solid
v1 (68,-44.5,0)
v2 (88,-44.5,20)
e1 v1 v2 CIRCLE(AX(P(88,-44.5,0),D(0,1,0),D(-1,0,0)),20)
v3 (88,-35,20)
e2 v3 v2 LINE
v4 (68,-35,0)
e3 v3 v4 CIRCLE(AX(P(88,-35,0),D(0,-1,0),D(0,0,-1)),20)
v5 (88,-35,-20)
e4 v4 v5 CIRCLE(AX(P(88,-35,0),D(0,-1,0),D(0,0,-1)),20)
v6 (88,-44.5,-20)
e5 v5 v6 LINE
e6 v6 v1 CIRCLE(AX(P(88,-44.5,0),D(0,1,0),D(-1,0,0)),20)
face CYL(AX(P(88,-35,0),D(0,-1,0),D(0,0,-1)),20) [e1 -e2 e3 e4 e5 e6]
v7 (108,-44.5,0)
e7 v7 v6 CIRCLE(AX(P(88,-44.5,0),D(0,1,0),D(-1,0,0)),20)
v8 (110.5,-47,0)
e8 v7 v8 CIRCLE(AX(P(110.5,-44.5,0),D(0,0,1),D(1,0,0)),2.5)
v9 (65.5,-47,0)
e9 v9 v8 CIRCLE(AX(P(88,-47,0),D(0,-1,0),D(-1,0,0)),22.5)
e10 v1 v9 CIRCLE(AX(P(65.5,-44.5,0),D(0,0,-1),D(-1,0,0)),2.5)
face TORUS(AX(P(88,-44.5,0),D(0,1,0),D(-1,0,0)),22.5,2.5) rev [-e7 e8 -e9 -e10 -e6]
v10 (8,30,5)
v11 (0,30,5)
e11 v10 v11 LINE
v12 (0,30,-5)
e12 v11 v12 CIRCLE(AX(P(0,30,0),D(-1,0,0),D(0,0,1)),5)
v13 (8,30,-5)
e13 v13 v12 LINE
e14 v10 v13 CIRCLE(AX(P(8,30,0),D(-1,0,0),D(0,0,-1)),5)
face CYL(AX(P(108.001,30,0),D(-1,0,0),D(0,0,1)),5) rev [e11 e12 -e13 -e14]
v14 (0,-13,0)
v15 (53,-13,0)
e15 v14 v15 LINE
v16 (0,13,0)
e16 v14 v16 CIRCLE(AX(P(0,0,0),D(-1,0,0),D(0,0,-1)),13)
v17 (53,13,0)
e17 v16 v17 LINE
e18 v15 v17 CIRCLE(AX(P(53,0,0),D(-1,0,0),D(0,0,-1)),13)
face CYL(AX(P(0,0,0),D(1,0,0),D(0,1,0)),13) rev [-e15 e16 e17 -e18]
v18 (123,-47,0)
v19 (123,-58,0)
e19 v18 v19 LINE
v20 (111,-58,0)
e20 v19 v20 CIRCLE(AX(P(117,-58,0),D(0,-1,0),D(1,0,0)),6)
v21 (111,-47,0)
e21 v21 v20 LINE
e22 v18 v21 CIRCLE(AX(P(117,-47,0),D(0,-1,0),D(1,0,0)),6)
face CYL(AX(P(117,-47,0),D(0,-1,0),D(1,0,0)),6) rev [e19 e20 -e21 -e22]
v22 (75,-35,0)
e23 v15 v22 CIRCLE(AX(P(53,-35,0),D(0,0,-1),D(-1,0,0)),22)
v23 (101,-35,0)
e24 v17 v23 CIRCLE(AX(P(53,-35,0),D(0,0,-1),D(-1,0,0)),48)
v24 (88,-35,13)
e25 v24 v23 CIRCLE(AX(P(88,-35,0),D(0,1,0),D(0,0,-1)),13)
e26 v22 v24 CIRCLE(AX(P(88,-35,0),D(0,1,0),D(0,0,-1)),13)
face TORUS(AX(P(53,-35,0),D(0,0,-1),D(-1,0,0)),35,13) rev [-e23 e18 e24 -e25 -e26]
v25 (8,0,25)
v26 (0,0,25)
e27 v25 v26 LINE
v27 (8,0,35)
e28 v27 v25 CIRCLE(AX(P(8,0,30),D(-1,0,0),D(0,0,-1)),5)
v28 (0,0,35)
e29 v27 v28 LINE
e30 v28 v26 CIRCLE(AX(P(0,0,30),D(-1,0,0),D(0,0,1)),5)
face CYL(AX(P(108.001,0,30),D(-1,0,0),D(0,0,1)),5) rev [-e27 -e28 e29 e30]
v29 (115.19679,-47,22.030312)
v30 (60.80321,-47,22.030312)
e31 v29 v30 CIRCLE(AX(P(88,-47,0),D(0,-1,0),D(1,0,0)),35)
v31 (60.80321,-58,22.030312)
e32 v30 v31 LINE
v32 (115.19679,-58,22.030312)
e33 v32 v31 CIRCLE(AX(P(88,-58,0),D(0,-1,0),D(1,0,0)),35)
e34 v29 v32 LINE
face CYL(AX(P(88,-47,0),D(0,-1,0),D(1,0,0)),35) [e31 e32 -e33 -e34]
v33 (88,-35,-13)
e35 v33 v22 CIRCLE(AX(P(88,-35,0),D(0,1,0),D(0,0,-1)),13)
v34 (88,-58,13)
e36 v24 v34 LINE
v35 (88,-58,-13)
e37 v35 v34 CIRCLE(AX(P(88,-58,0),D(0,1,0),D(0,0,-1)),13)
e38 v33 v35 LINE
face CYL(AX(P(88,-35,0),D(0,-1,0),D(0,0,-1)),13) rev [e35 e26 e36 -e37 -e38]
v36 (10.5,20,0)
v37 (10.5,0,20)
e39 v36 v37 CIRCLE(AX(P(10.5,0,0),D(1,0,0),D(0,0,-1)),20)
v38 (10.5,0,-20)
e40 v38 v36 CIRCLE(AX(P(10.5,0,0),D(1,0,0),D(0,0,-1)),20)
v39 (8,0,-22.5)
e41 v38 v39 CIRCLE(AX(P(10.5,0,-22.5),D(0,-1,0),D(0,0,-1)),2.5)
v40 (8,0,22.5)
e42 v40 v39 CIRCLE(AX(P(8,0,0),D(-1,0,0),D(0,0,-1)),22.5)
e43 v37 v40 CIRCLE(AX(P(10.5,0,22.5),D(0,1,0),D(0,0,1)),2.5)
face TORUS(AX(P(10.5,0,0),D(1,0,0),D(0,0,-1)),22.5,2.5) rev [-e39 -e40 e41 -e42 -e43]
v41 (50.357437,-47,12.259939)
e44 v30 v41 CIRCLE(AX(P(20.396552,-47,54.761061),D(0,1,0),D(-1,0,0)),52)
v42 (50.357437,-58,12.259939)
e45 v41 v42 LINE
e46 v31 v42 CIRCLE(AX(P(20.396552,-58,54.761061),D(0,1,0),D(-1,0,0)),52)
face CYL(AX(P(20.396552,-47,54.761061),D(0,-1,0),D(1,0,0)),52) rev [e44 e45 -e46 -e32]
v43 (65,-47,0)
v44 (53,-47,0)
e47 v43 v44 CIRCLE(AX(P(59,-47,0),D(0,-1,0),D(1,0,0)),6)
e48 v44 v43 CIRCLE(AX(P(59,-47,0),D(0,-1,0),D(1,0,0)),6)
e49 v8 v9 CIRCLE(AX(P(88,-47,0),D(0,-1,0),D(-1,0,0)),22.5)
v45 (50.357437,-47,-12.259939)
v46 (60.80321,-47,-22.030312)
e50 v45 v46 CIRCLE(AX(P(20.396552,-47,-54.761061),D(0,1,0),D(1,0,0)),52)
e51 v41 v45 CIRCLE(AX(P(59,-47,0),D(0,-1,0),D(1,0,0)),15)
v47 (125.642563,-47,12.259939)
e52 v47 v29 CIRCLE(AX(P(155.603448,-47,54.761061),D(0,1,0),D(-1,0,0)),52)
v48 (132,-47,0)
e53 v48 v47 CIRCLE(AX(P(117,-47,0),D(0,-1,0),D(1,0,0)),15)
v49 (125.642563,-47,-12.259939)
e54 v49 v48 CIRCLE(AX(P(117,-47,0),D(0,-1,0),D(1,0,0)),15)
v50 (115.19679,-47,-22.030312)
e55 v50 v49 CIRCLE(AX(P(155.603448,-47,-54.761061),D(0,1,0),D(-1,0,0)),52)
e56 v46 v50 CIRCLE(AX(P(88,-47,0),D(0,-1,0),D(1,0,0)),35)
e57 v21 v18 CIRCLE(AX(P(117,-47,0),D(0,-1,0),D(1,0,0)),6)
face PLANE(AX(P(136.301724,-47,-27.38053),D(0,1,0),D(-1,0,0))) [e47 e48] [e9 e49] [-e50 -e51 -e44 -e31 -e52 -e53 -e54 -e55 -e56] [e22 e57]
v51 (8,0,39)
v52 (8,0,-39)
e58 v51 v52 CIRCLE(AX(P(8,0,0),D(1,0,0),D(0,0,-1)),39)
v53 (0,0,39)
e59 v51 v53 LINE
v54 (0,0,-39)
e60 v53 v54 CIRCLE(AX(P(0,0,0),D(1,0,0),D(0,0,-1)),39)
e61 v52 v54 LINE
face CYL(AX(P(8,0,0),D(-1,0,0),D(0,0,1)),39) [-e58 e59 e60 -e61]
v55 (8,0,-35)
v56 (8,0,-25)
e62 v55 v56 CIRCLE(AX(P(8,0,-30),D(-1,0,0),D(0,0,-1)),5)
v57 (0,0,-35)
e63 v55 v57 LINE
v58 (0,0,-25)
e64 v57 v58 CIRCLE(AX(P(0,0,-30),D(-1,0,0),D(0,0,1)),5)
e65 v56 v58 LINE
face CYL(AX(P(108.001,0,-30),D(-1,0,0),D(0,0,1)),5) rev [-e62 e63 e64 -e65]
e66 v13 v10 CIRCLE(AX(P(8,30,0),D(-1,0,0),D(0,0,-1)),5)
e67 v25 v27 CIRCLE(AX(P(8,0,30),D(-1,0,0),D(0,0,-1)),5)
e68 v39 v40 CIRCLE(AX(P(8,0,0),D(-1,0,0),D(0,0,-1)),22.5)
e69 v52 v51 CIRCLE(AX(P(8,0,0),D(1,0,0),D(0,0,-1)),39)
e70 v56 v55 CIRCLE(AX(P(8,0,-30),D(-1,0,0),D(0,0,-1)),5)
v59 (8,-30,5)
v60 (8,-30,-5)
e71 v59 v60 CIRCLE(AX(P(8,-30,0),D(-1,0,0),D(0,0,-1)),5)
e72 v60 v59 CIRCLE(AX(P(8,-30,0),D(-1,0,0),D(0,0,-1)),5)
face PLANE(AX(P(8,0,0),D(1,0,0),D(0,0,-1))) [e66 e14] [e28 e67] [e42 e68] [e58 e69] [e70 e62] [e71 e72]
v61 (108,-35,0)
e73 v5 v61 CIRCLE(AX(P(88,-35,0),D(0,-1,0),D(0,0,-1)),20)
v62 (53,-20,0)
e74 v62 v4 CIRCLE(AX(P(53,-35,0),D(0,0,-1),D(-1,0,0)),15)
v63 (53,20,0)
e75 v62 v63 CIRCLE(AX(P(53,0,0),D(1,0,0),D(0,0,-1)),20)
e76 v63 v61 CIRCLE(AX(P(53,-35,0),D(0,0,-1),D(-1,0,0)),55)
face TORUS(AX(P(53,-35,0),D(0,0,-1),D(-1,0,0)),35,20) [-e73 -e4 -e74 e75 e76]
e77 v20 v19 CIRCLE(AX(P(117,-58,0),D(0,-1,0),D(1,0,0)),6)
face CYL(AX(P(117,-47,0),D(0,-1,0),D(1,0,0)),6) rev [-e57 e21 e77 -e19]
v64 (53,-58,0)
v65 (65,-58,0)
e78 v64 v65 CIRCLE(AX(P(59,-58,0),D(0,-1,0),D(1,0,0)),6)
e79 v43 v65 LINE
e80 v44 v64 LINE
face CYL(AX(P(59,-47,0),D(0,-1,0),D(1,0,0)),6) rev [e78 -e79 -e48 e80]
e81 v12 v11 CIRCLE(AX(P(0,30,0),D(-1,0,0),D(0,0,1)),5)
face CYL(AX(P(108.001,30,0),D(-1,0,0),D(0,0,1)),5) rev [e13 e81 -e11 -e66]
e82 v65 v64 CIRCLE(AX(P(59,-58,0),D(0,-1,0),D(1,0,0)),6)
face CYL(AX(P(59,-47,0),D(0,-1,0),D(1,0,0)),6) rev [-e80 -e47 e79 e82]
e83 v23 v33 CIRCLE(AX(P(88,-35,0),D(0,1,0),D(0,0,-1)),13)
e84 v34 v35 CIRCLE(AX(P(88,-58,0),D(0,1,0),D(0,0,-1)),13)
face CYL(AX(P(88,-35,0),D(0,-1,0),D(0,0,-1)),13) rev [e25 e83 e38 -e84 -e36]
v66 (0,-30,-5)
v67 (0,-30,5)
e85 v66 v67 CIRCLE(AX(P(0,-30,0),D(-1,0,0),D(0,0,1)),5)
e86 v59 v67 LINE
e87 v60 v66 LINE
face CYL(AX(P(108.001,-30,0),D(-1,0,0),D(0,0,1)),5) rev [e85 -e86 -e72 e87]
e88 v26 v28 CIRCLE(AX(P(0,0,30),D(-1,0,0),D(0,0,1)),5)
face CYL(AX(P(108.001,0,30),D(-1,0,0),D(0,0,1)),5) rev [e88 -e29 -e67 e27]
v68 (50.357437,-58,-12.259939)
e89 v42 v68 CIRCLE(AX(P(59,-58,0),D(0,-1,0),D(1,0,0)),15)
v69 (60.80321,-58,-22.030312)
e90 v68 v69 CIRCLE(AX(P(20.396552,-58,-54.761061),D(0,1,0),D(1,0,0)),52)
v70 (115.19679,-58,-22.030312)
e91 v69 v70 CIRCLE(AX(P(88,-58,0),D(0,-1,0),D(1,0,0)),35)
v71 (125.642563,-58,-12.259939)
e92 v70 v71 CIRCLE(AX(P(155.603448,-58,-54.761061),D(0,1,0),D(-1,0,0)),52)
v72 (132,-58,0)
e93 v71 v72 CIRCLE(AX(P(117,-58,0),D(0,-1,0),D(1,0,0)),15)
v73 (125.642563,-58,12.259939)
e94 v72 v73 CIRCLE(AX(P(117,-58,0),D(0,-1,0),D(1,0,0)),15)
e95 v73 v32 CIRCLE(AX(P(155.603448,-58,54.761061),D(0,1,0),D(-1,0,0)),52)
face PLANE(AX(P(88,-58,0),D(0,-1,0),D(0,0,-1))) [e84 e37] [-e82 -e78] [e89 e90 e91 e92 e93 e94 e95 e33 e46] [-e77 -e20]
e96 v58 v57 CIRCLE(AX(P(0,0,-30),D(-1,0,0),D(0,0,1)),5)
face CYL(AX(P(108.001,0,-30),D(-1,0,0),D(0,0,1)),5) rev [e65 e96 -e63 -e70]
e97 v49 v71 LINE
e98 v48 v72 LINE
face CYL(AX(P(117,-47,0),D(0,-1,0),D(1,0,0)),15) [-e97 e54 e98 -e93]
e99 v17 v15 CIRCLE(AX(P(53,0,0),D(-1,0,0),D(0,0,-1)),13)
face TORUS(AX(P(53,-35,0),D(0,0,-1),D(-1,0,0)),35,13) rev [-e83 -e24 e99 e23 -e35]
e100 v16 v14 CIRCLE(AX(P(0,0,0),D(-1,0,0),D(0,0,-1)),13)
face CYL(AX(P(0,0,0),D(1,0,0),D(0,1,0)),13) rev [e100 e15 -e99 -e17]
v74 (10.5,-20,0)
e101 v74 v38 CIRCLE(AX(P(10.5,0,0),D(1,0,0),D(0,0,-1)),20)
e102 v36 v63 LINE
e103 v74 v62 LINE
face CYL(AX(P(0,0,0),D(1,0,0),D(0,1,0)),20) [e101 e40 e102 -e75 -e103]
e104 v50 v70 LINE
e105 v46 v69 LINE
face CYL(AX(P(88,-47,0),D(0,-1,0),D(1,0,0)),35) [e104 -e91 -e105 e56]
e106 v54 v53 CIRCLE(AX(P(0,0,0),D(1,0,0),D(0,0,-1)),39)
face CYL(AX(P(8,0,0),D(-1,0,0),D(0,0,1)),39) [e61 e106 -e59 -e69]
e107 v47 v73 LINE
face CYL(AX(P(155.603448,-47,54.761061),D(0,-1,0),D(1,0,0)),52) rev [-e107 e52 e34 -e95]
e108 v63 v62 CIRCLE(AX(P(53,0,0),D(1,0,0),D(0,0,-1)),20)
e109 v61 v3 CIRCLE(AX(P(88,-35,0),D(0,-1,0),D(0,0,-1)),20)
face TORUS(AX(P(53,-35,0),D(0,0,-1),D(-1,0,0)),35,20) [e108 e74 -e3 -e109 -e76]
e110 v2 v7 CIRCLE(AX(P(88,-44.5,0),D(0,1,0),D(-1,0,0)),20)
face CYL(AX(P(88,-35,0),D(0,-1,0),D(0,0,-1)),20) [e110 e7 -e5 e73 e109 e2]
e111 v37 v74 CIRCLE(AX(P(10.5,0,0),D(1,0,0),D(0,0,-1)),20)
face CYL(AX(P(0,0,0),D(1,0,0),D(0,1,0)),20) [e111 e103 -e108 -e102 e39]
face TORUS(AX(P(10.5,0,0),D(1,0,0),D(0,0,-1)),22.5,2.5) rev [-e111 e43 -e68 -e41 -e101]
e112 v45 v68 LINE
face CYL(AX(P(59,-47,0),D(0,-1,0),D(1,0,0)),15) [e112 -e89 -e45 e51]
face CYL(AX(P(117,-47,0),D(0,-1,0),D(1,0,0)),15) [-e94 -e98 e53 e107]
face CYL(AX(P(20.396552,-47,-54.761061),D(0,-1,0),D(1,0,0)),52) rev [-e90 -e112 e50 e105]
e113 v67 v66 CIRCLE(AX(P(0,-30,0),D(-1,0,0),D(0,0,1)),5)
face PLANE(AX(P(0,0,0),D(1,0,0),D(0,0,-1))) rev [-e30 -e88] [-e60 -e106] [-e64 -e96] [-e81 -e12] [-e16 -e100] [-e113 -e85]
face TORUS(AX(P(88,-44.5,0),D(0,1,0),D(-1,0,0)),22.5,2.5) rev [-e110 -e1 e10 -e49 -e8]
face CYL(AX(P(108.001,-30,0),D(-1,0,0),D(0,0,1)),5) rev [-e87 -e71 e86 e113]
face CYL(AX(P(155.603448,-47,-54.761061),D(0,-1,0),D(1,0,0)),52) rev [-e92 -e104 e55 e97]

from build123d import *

# Parameters (mm, degrees)
PIPE_SECTION_SKETCH_40X_26_R        = 20
PIPE_SECTION_SKETCH_40X_26_R_2      = 13
ROUND_START                         = 8
ROUND_FLANGE_SKETCH_78_R            = 39
ROUND_FLANGE_SKETCH_78_R_2          = 13
ROUND_FLANGE_78_DEPTH               = 8
ROUND_FLANGE_BOLT_HOLES_4X_10_REACH = 130.643
ROUND_FLANGE_BOLT_HOLES_SKETCH_R    = 5
OVAL_FLANGE_SKETCH_R                = 6
OVAL_FLANGE_SKETCH_R_2              = 13
OVAL_FLANGE_DEPTH                   = 11
FLANGE_ROOT_FILLETS_R2_5_R          = 2.5


with BuildPart() as part:
    # Elbow Pipe Body: sweep along a path in Elbow Path Sketch
    with BuildLine(Plane.XY) as elbow_pipe_body_path:
        Line((0, 0), (53, 0))
        ThreePointArc((53, 0), (77.748737342, -10.251262658), (88, -35))
        Line((88, -35), (88, -58))
    # Pipe Section Sketch Ø40xØ26 → Elbow Pipe Body (sweep)
    with BuildSketch(Plane(origin=(0, 0, 0), x_dir=(0, 0, -1), z_dir=(1, 0, 0))):
        Circle(PIPE_SECTION_SKETCH_40X_26_R)
        Circle(PIPE_SECTION_SKETCH_40X_26_R_2, mode=Mode.SUBTRACT)
    sweep(path=elbow_pipe_body_path.line)

    # Round Flange Sketch Ø78 → Round Flange Ø78 (add)
    with BuildSketch(Plane(origin=(0, 0, 0), x_dir=(0, 0, -1), z_dir=(1, 0, 0)).offset(ROUND_START)):
        Circle(ROUND_FLANGE_SKETCH_78_R)
        with Locations(Location((0, 0, 0), (0, 0, 90))):
            Circle(ROUND_FLANGE_SKETCH_78_R_2, mode=Mode.SUBTRACT)
    extrude(amount=-ROUND_FLANGE_78_DEPTH)

    # Round Flange Bolt Holes Sketch → Round Flange Bolt Holes 4xØ10 (cut, up to next)
    with BuildSketch(Plane.ZY, mode=Mode.PRIVATE) as round_flange_bolt_holes_4x_10_sk1:
        with Locations((0, 30)):
            Circle(ROUND_FLANGE_BOLT_HOLES_SKETCH_R)
    round_flange_bolt_holes_4x_10_tool1 = extrude(round_flange_bolt_holes_4x_10_sk1.sketch, amount=-ROUND_FLANGE_BOLT_HOLES_4X_10_REACH, mode=Mode.PRIVATE) & part.part
    # Round Flange Bolt Holes Sketch → Round Flange Bolt Holes 4xØ10 (cut, up to next)
    with BuildSketch(Plane.ZY, mode=Mode.PRIVATE) as round_flange_bolt_holes_4x_10_sk2:
        with Locations((30, 0)):
            Circle(ROUND_FLANGE_BOLT_HOLES_SKETCH_R)
    round_flange_bolt_holes_4x_10_tool2 = extrude(round_flange_bolt_holes_4x_10_sk2.sketch, amount=-ROUND_FLANGE_BOLT_HOLES_4X_10_REACH, mode=Mode.PRIVATE) & part.part
    # Round Flange Bolt Holes Sketch → Round Flange Bolt Holes 4xØ10 (cut, up to next)
    with BuildSketch(Plane.ZY, mode=Mode.PRIVATE) as round_flange_bolt_holes_4x_10_sk3:
        with Locations((0, -30)):
            Circle(ROUND_FLANGE_BOLT_HOLES_SKETCH_R)
    round_flange_bolt_holes_4x_10_tool3 = extrude(round_flange_bolt_holes_4x_10_sk3.sketch, amount=-ROUND_FLANGE_BOLT_HOLES_4X_10_REACH, mode=Mode.PRIVATE) & part.part
    # Round Flange Bolt Holes Sketch → Round Flange Bolt Holes 4xØ10 (cut, up to next)
    with BuildSketch(Plane.ZY, mode=Mode.PRIVATE) as round_flange_bolt_holes_4x_10_sk4:
        with Locations((-30, 0)):
            Circle(ROUND_FLANGE_BOLT_HOLES_SKETCH_R)
    round_flange_bolt_holes_4x_10_tool4 = extrude(round_flange_bolt_holes_4x_10_sk4.sketch, amount=-ROUND_FLANGE_BOLT_HOLES_4X_10_REACH, mode=Mode.PRIVATE) & part.part
    add(round_flange_bolt_holes_4x_10_tool1.solids().sort_by_distance((0, 30, 0))[0], mode=Mode.SUBTRACT)
    add(round_flange_bolt_holes_4x_10_tool2.solids().sort_by_distance((0, 0, 30))[0], mode=Mode.SUBTRACT)
    add(round_flange_bolt_holes_4x_10_tool3.solids().sort_by_distance((0, -30, 0))[0], mode=Mode.SUBTRACT)
    add(round_flange_bolt_holes_4x_10_tool4.solids().sort_by_distance((0, 0, -30))[0], mode=Mode.SUBTRACT)

    # Oval Flange Sketch → Oval Flange (add)
    with BuildSketch(Plane.XZ.offset(58)):
        with BuildLine():
            ThreePointArc((60.803210464, -22.030311821), (88, -35), (115.196789536, -22.030311821))
            ThreePointArc((115.196789536, -22.030311821), (120.082146816, -16.784263387), (125.642563047, -12.259938988))
            ThreePointArc((125.642563047, -12.259938988), (132, 0), (125.642563047, 12.259938988))
            ThreePointArc((125.642563047, 12.259938988), (120.082146816, 16.784263387), (115.196789536, 22.030311821))
            ThreePointArc((115.196789536, 22.030311821), (88, 35), (60.803210464, 22.030311821))
            ThreePointArc((60.803210464, 22.030311821), (55.917853184, 16.784263387), (50.357436953, 12.259938988))
            ThreePointArc((50.357436953, 12.259938988), (44, 0), (50.357436953, -12.259938988))
            ThreePointArc((50.357436953, -12.259938988), (55.917853184, -16.784263387), (60.803210464, -22.030311821))
        make_face()
        with Locations((117, 0)):
            Circle(OVAL_FLANGE_SKETCH_R, mode=Mode.SUBTRACT)
        with Locations((59, 0)):
            Circle(OVAL_FLANGE_SKETCH_R, mode=Mode.SUBTRACT)
        with Locations(Location((88, 0, 0), (0, 0, 270))):
            Circle(OVAL_FLANGE_SKETCH_R_2, mode=Mode.SUBTRACT)
    extrude(amount=-OVAL_FLANGE_DEPTH)

    # Flange Root Fillets R2.5
    flange_root_fillets_r2_5_edges = [part.edges().sort_by_distance(p)[0] for p in [
        (8, 0, 20),
        (88, -47, 20),
    ]]
    fillet(flange_root_fillets_r2_5_edges, radius=FLANGE_ROOT_FILLETS_R2_5_R)


solid = part.part
